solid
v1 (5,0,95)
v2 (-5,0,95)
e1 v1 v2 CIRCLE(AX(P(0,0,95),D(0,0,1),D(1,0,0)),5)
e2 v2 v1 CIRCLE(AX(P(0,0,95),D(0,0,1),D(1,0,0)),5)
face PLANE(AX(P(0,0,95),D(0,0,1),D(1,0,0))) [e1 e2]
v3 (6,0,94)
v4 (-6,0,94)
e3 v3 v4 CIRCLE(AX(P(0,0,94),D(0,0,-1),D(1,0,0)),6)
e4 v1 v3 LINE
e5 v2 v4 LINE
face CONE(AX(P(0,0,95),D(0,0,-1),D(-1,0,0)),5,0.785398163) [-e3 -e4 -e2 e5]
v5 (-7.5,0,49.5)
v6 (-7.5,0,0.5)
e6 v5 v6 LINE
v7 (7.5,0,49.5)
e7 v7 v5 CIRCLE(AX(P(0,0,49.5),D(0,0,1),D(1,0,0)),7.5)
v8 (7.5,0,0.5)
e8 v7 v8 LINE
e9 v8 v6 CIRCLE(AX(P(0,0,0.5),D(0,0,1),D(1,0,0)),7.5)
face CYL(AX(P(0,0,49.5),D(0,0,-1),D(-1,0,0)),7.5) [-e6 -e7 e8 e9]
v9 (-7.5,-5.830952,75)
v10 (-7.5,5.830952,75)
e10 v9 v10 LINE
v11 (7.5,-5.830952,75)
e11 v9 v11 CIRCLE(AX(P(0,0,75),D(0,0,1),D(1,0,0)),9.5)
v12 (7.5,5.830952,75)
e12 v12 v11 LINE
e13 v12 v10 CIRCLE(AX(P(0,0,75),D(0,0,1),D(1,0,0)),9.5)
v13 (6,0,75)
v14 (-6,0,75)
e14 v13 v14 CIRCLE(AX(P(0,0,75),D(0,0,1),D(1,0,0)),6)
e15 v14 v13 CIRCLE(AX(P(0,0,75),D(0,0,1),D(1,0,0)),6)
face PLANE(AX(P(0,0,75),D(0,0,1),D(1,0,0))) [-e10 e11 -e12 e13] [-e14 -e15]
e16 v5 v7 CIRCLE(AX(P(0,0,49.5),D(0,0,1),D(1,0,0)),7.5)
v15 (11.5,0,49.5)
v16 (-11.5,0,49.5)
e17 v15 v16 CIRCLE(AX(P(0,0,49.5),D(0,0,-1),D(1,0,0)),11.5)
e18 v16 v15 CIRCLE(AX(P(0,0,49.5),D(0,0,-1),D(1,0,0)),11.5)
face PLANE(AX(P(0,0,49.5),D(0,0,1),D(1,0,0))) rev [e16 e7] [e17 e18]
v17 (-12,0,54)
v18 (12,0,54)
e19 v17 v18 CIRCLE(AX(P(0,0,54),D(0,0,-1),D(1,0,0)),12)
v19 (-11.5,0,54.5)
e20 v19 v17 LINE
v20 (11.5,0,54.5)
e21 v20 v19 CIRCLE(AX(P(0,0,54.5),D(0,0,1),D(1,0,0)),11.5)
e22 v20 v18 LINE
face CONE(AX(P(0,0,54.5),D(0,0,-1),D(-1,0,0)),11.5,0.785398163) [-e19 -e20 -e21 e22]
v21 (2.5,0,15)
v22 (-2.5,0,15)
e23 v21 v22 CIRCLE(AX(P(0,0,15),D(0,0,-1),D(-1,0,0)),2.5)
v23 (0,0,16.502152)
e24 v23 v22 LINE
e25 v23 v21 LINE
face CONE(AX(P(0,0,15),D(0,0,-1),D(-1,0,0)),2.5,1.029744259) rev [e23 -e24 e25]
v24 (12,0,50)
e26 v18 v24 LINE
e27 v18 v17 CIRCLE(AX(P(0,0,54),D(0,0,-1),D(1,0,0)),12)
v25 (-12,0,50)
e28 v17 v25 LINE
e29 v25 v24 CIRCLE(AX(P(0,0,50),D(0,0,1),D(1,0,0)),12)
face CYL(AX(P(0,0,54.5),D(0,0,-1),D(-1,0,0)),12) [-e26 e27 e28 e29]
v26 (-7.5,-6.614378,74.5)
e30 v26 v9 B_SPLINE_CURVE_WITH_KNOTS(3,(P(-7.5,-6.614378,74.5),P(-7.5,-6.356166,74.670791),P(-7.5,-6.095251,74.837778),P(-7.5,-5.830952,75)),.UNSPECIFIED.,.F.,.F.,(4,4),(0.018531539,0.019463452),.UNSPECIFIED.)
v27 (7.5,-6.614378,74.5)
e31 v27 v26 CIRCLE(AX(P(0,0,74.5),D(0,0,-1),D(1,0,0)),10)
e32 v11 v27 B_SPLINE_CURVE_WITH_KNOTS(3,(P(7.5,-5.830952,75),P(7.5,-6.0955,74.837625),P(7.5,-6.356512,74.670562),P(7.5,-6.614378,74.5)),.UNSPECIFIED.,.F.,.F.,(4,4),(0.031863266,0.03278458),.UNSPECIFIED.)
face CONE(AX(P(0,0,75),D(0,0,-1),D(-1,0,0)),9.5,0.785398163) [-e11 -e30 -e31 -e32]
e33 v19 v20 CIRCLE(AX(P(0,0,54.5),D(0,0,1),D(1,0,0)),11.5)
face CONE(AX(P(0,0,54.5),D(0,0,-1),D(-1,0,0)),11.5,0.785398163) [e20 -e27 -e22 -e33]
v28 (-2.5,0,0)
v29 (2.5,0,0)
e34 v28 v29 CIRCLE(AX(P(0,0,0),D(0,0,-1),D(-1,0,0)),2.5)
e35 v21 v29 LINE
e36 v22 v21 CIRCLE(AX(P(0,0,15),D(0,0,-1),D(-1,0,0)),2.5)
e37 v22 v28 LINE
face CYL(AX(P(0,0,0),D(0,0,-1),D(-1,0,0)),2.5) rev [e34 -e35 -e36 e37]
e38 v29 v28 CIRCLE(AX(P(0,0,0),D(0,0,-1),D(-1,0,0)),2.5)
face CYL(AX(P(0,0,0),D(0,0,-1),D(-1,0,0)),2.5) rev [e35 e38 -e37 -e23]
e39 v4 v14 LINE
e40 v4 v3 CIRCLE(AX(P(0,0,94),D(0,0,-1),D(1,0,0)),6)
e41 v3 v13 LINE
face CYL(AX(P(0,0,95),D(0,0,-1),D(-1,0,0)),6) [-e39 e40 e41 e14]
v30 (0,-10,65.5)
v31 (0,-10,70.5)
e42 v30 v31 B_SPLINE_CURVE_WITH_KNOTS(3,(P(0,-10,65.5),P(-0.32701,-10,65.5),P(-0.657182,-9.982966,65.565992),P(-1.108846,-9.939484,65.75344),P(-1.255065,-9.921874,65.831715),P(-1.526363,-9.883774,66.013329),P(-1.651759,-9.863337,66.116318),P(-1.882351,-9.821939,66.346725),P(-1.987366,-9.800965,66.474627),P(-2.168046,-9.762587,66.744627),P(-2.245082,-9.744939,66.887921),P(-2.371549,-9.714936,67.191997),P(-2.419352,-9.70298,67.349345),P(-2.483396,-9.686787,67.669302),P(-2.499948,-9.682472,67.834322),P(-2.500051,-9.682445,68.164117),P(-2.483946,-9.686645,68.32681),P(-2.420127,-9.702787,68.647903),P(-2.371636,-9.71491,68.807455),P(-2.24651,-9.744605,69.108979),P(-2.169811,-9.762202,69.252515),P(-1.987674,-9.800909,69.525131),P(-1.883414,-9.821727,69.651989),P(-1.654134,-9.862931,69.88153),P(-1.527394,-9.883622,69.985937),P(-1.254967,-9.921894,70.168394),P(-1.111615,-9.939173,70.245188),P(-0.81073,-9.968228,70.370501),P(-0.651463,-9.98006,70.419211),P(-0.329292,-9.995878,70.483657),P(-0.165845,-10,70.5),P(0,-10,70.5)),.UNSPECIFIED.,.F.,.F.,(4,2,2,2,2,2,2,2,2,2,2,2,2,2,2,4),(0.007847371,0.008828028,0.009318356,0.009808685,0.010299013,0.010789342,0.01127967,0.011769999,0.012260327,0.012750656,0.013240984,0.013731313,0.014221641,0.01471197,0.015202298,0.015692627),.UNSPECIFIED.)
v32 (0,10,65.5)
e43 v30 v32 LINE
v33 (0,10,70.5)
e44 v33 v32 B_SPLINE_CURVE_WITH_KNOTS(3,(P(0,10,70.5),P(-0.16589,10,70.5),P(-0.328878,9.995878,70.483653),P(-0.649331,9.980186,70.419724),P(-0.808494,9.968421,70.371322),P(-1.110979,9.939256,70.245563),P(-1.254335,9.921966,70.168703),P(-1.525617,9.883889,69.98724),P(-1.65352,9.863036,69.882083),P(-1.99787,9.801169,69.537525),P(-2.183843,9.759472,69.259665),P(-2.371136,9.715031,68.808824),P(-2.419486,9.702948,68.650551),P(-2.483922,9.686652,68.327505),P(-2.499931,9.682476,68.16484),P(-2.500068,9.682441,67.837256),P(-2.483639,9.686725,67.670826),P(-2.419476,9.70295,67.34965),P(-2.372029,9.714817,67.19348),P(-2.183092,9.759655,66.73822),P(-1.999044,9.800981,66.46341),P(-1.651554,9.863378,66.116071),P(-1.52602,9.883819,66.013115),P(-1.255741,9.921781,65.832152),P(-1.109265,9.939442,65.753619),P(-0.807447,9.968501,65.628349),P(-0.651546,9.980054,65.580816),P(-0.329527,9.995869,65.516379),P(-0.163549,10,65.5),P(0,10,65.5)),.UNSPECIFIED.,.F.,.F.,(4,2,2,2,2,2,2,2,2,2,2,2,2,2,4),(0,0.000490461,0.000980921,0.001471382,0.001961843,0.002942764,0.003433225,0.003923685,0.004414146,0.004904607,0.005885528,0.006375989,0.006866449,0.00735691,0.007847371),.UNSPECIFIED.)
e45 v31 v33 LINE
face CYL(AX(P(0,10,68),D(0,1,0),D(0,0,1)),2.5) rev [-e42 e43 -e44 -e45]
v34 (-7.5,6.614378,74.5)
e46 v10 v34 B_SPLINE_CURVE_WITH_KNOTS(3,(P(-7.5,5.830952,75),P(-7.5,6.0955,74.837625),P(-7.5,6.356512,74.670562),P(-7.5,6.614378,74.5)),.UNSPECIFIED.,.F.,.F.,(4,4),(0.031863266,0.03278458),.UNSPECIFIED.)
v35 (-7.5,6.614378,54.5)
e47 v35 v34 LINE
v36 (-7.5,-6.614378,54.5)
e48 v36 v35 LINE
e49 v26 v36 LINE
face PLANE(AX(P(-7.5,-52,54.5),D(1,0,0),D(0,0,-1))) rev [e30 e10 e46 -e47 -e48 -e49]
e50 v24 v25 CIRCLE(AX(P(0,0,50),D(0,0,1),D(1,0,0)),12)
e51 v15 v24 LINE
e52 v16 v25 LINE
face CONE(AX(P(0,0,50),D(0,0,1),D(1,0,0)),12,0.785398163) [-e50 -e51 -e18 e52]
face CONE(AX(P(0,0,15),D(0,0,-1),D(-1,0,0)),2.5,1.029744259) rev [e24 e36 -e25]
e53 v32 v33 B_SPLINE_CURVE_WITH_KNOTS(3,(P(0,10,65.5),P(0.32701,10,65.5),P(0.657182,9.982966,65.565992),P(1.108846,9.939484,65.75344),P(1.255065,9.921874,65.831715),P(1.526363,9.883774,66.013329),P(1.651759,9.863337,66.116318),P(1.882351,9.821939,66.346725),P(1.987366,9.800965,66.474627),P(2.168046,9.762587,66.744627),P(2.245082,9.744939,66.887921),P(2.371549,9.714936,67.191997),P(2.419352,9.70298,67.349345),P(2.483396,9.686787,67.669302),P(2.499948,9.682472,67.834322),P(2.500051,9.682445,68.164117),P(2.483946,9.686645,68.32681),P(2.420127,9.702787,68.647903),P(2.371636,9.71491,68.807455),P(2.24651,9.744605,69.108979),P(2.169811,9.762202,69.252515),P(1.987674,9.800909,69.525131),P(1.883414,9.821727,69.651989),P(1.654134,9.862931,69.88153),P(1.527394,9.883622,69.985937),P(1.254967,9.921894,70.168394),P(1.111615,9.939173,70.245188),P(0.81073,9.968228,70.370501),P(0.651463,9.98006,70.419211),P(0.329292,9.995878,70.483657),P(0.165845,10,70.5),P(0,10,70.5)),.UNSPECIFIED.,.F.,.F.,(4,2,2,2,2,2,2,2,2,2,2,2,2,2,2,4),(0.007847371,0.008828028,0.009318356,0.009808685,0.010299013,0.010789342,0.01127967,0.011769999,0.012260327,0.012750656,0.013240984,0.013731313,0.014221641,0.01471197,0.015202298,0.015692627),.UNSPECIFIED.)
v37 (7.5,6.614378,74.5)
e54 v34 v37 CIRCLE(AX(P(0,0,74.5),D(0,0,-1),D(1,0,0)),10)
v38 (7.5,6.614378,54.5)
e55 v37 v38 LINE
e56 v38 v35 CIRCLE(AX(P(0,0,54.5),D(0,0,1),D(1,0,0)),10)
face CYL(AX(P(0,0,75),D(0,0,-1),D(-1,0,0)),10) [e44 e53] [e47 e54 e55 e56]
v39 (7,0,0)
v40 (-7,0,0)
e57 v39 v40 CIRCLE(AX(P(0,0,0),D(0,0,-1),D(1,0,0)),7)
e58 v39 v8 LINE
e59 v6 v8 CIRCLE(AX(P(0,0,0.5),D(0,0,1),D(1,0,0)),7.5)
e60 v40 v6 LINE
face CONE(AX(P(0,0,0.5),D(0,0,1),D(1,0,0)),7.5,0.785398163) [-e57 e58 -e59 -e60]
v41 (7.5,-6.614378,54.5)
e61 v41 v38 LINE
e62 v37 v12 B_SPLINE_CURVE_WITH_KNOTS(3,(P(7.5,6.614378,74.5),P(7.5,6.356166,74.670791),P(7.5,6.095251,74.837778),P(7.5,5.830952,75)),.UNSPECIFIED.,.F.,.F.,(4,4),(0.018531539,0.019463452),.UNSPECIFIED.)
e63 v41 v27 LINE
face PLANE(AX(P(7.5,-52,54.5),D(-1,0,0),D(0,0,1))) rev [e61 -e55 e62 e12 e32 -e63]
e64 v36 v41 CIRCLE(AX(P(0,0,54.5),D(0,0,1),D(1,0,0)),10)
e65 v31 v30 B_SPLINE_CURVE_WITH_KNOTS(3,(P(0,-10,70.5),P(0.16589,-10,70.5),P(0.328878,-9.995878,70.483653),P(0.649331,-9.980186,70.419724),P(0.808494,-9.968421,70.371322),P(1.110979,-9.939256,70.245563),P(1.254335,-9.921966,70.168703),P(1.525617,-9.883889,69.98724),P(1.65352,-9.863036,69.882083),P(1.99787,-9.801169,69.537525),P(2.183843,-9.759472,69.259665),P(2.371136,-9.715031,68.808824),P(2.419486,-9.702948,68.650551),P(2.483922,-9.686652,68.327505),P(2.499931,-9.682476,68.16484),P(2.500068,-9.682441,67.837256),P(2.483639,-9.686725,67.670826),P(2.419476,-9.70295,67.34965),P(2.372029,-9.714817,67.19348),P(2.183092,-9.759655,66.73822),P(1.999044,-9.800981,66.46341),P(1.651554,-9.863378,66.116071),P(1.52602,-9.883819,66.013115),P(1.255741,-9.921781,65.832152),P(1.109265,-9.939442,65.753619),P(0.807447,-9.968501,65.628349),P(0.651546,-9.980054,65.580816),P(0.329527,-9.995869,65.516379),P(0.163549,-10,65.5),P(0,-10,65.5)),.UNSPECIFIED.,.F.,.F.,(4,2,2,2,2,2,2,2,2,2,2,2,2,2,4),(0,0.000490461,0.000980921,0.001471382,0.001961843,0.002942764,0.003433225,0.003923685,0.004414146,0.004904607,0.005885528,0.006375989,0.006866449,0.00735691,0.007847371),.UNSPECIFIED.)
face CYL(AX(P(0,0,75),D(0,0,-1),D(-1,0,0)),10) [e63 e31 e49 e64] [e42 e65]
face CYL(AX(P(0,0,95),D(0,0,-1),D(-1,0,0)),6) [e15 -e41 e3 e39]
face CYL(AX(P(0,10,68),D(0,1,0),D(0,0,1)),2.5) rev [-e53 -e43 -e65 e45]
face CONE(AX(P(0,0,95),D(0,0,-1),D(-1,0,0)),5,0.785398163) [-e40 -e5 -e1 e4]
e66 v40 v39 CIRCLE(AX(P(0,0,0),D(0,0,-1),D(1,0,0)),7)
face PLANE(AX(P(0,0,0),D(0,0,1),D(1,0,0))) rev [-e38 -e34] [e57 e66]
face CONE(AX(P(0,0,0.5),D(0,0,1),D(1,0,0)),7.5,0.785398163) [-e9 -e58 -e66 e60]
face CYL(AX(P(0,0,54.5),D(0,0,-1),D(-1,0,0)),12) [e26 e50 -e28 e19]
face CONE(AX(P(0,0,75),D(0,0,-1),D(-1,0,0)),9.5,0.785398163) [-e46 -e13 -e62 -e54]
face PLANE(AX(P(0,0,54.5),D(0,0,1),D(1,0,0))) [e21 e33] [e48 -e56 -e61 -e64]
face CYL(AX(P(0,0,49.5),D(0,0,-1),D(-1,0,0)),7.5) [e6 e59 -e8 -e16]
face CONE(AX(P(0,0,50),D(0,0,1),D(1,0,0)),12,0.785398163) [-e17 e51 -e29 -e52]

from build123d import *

# Parameters (mm, degrees)
SKETCH_1_R             = 7.5
EXTRUDE_1_DEPTH        = 49.5
SKETCH_2_R             = 12
EXTRUDE_2_DEPTH        = 5
SKETCH_3_R             = 10
EXTRUDE_3_DEPTH        = 20.5
SKETCH_4_R             = 6
EXTRUDE_4_DEPTH        = 20
HOLE_WIZARD_M6_1_D     = 5
HOLE_WIZARD_M6_1_DEPTH = 15
HOLE_WIZARD_M6_1_TIP   = 1.502151548
CHAMFER_1_SIZE         = 0.5
CHAMFER_2_SIZE         = 1
CHAMFER_3_SIZE         = 0.5
SKETCH_7_W             = 26.460285879
SKETCH_7_H             = 26.47281766
SKETCH_7_W_2           = 19.498728734
SKETCH_7_H_2           = 28.747669346
CUT_EXTRUDE_1_DEPTH    = 52
HOLE_WIZARD_M6_2_D     = 5


with BuildPart() as part:
    # 草图1 → 凸台-拉伸1 (new body)
    with BuildSketch(Plane.XY):
        Circle(SKETCH_1_R)
    extrude(amount=EXTRUDE_1_DEPTH)

    # 草图2 → 凸台-拉伸2 (add)
    with BuildSketch(Plane.XY.offset(49.5)):
        Circle(SKETCH_2_R)
    extrude(amount=EXTRUDE_2_DEPTH)

    # 草图3 → 凸台-拉伸3 (add)
    with BuildSketch(Plane.XY.offset(54.5)):
        Circle(SKETCH_3_R)
    extrude(amount=EXTRUDE_3_DEPTH)

    # 草图4 → 凸台-拉伸4 (add)
    with BuildSketch(Plane.XY.offset(75)):
        Circle(SKETCH_4_R)
    extrude(amount=EXTRUDE_4_DEPTH)

    # M6 螺纹孔1
    with Locations(Plane(origin=(0, 0, 0), x_dir=(-1, 0, 0), z_dir=(0, 0, -1))):
        with Locations((0, 0)):
            Hole(HOLE_WIZARD_M6_1_D / 2, depth=HOLE_WIZARD_M6_1_DEPTH)
            with Locations((0, 0, -(HOLE_WIZARD_M6_1_DEPTH + HOLE_WIZARD_M6_1_TIP / 2))):  # 118° drill point
                Cone(0, HOLE_WIZARD_M6_1_D / 2, HOLE_WIZARD_M6_1_TIP, mode=Mode.SUBTRACT)

    # 倒角1
    chamfer_1_edges = [part.edges().sort_by_distance(p)[0] for p in [
        (-7.5, 0, 0),
        (-12, 0, 49.5),
        (-12, 0, 54.5),
    ]]
    chamfer(chamfer_1_edges, length=CHAMFER_1_SIZE)

    # 倒角2
    chamfer_2_edges = [part.edges().sort_by_distance(p)[0] for p in [
        (-6, 0, 95),
    ]]
    chamfer(chamfer_2_edges, length=CHAMFER_2_SIZE)

    # 倒角3
    chamfer_3_edges = [part.edges().sort_by_distance(p)[0] for p in [
        (-10, 0, 75),
    ]]
    chamfer(chamfer_3_edges, length=CHAMFER_3_SIZE)

    # 草图7 → 切除-拉伸1 (cut, symmetric)
    with BuildSketch(Plane(origin=(0, 0, 0), x_dir=(1, 0, 0), z_dir=(0, 1, 0))):
        with Locations((-20.73014294, -67.73640883)):
            Rectangle(SKETCH_7_W, SKETCH_7_H)
        with Locations((17.249364367, -68.873834673)):
            Rectangle(SKETCH_7_W_2, SKETCH_7_H_2)
    extrude(amount=CUT_EXTRUDE_1_DEPTH, both=True, mode=Mode.SUBTRACT)

    # M6 螺纹孔2 (through all)
    with Locations(Plane(origin=(0, 10, 0), x_dir=(1, 0, 0), z_dir=(0, 1, 0))):
        with Locations((0, -68)):
            Hole(HOLE_WIZARD_M6_2_D / 2)


solid = part.part
